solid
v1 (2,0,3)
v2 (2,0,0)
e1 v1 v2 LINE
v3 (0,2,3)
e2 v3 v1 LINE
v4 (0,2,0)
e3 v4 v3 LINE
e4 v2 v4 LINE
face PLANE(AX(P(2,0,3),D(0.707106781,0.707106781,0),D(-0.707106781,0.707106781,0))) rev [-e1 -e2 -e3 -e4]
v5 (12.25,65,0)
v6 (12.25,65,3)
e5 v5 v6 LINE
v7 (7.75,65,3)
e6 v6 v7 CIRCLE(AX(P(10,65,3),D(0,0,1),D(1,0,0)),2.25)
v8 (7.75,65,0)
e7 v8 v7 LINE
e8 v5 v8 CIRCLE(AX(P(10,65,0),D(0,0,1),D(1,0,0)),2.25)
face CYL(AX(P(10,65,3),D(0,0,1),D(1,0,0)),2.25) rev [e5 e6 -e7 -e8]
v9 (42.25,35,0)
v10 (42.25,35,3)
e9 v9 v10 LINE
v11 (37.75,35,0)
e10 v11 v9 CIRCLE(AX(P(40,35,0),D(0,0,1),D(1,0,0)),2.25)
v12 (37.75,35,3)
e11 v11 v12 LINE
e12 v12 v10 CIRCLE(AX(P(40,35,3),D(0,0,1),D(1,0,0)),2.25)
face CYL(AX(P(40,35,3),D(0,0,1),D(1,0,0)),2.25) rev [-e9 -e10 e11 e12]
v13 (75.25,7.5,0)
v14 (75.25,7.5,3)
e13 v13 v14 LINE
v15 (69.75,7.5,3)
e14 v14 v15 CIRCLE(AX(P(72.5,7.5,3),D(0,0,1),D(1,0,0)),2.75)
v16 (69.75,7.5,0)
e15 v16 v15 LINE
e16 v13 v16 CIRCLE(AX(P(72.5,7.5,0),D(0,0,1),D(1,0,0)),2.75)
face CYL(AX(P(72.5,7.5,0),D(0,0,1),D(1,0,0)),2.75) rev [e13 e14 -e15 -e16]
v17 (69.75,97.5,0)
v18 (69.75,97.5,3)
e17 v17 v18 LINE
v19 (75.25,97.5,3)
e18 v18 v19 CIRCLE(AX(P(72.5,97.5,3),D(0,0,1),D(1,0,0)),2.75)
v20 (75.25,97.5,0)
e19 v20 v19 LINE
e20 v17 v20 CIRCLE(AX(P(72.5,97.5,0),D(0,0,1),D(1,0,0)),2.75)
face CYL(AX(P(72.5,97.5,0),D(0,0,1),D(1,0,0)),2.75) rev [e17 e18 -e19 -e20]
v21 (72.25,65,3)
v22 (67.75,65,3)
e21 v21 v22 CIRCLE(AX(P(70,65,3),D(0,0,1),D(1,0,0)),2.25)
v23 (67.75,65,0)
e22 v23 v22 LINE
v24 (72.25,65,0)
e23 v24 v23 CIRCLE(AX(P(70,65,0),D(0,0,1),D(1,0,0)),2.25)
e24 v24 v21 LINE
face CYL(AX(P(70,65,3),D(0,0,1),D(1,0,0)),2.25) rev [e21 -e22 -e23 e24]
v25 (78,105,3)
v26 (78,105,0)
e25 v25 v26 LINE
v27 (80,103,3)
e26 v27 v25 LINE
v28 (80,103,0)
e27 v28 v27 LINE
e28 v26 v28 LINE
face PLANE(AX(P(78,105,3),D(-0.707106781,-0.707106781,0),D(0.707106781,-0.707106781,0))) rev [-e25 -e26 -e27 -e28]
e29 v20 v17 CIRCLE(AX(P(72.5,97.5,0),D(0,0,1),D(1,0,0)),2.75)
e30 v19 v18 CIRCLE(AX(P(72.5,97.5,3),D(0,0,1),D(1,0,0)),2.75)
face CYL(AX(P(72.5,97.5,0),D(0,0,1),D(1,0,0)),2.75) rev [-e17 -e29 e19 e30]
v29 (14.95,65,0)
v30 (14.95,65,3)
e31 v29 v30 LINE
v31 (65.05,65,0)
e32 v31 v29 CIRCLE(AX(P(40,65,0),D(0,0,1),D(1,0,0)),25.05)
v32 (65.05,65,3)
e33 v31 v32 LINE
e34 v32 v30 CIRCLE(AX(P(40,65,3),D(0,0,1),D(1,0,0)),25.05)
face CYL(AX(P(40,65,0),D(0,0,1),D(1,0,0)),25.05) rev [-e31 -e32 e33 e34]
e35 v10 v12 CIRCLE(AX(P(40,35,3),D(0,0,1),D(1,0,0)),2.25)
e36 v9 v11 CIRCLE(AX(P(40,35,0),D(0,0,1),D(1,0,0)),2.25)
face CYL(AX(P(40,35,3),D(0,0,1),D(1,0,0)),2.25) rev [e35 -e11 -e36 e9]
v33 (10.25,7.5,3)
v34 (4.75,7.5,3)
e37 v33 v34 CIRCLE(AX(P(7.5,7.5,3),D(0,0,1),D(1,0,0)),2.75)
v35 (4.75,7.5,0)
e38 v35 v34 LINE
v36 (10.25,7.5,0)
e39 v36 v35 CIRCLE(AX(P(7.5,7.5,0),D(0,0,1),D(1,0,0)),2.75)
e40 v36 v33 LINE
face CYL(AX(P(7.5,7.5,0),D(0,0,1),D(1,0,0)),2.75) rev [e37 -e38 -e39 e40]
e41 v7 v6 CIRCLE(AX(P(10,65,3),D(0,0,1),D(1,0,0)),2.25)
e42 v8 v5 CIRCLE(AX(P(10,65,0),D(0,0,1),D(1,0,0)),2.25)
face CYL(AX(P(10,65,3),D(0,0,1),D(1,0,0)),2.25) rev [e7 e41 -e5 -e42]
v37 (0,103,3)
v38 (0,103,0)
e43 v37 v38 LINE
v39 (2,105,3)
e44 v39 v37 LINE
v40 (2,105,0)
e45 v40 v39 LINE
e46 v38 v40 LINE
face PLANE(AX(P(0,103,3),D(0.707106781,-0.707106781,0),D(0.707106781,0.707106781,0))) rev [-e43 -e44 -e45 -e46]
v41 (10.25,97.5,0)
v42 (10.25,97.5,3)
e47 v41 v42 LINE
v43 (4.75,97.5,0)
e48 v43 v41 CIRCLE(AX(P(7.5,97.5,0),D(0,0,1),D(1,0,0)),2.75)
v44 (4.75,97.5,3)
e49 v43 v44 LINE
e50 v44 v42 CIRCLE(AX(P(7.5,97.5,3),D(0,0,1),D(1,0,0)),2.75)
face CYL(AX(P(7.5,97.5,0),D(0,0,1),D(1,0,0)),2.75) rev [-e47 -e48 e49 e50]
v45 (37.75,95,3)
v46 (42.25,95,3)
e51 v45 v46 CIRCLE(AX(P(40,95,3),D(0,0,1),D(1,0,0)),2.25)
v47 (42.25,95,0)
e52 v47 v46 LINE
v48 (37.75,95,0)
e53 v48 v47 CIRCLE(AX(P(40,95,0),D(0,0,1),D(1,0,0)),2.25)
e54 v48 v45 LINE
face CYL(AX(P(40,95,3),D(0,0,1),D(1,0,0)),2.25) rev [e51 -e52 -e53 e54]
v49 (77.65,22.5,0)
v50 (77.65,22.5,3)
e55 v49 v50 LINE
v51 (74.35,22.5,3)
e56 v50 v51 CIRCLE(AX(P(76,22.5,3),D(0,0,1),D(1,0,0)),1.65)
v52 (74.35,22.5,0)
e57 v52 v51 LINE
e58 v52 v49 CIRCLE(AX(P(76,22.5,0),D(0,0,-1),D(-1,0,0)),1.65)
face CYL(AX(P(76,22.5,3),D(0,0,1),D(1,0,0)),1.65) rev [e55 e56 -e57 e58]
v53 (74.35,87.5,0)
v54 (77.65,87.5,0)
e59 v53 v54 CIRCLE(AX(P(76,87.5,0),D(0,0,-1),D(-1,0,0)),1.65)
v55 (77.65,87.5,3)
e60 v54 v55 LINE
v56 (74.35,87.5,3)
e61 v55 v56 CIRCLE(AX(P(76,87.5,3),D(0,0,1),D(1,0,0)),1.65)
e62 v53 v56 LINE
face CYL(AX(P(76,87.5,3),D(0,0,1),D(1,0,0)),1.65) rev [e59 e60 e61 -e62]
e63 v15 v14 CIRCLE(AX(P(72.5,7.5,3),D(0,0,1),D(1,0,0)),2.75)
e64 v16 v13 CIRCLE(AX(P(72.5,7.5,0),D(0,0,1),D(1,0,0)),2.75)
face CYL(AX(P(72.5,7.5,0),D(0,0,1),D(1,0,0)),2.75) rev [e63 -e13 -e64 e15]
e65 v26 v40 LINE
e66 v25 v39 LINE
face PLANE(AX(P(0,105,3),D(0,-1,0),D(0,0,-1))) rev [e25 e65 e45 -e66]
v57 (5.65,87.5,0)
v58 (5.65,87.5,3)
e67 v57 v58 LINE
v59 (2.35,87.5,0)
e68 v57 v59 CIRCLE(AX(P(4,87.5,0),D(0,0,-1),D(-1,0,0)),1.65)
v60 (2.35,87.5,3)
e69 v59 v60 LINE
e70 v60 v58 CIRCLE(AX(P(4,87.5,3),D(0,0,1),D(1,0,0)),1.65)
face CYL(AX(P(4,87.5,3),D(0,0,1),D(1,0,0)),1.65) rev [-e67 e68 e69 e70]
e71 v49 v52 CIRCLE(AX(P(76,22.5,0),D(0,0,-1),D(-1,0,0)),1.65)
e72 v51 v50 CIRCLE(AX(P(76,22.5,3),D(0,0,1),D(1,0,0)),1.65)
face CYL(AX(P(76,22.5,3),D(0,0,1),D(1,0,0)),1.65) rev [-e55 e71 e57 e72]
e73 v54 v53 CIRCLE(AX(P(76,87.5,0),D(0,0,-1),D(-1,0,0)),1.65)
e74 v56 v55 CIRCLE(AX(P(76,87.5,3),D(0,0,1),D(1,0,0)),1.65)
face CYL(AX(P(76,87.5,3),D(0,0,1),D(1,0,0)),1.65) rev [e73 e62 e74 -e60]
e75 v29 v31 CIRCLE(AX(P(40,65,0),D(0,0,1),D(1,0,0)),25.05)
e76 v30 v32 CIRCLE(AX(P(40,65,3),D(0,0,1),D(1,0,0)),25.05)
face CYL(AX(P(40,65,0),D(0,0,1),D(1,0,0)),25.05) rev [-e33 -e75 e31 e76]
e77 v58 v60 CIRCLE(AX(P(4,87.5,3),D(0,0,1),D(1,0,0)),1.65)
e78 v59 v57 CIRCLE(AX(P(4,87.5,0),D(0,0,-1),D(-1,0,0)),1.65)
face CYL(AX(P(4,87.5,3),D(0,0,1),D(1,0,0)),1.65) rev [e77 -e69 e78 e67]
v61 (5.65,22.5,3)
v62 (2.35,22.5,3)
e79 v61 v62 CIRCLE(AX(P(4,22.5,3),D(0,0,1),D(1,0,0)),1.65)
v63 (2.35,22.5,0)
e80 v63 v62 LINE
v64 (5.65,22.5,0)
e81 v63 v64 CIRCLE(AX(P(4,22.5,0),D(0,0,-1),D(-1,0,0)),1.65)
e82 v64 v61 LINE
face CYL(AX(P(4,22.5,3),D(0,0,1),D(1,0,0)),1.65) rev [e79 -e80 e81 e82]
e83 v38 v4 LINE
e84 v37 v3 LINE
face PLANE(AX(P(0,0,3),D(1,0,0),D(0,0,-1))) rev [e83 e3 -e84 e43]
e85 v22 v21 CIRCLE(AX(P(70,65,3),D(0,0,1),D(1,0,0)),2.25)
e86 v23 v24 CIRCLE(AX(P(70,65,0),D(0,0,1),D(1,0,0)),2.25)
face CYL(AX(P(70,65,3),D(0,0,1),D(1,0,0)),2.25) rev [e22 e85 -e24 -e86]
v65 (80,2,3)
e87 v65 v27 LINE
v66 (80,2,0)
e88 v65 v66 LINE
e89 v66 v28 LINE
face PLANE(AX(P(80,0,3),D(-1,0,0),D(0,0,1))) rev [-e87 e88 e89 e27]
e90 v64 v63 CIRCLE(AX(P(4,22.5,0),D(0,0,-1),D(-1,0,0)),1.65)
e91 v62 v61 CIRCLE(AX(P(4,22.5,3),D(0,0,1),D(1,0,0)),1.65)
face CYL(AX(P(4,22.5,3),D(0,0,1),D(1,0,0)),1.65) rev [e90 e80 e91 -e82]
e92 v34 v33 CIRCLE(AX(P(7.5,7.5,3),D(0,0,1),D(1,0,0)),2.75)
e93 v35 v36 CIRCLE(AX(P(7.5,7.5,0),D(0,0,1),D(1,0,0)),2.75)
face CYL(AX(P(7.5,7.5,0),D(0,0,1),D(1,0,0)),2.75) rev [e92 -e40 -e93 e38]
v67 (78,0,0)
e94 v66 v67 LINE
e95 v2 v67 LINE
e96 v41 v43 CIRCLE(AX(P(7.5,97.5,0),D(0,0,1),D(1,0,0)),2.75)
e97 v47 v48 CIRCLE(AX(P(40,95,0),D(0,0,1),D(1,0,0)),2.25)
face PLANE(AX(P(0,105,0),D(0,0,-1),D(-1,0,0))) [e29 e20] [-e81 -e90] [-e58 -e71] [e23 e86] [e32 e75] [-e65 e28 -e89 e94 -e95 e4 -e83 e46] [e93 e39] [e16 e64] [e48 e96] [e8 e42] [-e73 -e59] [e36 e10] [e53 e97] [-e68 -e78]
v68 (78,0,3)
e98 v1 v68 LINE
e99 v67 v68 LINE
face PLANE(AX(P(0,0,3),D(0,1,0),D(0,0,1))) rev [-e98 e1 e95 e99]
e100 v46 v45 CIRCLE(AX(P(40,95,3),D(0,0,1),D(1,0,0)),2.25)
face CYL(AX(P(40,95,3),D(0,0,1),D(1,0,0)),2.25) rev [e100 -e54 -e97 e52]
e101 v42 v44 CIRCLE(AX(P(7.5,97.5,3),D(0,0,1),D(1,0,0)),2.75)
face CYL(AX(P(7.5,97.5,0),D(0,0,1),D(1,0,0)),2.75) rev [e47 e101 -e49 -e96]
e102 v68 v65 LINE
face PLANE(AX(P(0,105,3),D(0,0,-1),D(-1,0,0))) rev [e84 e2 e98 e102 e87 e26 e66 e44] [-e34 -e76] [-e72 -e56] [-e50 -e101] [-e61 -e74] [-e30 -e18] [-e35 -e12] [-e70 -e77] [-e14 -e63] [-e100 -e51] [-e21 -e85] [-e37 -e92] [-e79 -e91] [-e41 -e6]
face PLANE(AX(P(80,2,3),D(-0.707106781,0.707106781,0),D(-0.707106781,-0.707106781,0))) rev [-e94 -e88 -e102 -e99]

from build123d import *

# Parameters (mm, degrees)
SKETCH1_W                  = 80
SKETCH1_H                  = 105
BOSS_EXTRUDE1_DEPTH        = 3
SKETCH2_R                  = 2.75
SKETCH2_R_2                = 25.05
CUT_EXTRUDE1_DEPTH         = 133.037873355
F_4_5_4_5_DIAMETER_HOLE1_D = 4.5
CHAMFER1_SIZE              = 2
M4_TAPPED_HOLE1_D          = 3.3
M4_TAPPED_HOLE1_DEPTH      = 10.1
M4_TAPPED_HOLE1_TIP        = 0.991420021


with BuildPart() as part:
    # Sketch1 → Boss-Extrude1 (new body)
    with BuildSketch(Plane.XY):
        with Locations((40, 52.5)):
            Rectangle(SKETCH1_W, SKETCH1_H)
    extrude(amount=BOSS_EXTRUDE1_DEPTH)

    # Sketch2 → Cut-Extrude1 (cut, through all)
    with BuildSketch(Plane.XY.offset(3)):
        with Locations((7.5, 97.5)):
            Circle(SKETCH2_R)
        with Locations((72.5, 97.5)):
            Circle(SKETCH2_R)
        with Locations((72.5, 7.5)):
            Circle(SKETCH2_R)
        with Locations((7.5, 7.5)):
            Circle(SKETCH2_R)
        with Locations((40, 65)):
            Circle(SKETCH2_R_2)
    extrude(amount=-CUT_EXTRUDE1_DEPTH, mode=Mode.SUBTRACT)

    # Ø4.5 (4.5) Diameter Hole1 (through all)
    with Locations(Plane.XY.offset(3)):
        with Locations((40, 95), (10, 65), (70, 65), (40, 35)):
            Hole(F_4_5_4_5_DIAMETER_HOLE1_D / 2)

    # Chamfer1
    chamfer1_edges = [part.edges().sort_by_distance(p)[0] for p in [
        (0, 105, 1.5),
        (80, 105, 1.5),
        (80, 0, 1.5),
        (0, 0, 1.5),
    ]]
    chamfer(chamfer1_edges, length=CHAMFER1_SIZE)

    # M4 Tapped Hole1
    with Locations(Plane.XY.offset(3)):
        with Locations((4, 87.5), (76, 87.5), (76, 22.5), (4, 22.5), (40, 65)):
            Hole(M4_TAPPED_HOLE1_D / 2, depth=M4_TAPPED_HOLE1_DEPTH)
            with Locations((0, 0, -(M4_TAPPED_HOLE1_DEPTH + M4_TAPPED_HOLE1_TIP / 2))):  # 118° drill point
                Cone(0, M4_TAPPED_HOLE1_D / 2, M4_TAPPED_HOLE1_TIP, mode=Mode.SUBTRACT)


solid = part.part
